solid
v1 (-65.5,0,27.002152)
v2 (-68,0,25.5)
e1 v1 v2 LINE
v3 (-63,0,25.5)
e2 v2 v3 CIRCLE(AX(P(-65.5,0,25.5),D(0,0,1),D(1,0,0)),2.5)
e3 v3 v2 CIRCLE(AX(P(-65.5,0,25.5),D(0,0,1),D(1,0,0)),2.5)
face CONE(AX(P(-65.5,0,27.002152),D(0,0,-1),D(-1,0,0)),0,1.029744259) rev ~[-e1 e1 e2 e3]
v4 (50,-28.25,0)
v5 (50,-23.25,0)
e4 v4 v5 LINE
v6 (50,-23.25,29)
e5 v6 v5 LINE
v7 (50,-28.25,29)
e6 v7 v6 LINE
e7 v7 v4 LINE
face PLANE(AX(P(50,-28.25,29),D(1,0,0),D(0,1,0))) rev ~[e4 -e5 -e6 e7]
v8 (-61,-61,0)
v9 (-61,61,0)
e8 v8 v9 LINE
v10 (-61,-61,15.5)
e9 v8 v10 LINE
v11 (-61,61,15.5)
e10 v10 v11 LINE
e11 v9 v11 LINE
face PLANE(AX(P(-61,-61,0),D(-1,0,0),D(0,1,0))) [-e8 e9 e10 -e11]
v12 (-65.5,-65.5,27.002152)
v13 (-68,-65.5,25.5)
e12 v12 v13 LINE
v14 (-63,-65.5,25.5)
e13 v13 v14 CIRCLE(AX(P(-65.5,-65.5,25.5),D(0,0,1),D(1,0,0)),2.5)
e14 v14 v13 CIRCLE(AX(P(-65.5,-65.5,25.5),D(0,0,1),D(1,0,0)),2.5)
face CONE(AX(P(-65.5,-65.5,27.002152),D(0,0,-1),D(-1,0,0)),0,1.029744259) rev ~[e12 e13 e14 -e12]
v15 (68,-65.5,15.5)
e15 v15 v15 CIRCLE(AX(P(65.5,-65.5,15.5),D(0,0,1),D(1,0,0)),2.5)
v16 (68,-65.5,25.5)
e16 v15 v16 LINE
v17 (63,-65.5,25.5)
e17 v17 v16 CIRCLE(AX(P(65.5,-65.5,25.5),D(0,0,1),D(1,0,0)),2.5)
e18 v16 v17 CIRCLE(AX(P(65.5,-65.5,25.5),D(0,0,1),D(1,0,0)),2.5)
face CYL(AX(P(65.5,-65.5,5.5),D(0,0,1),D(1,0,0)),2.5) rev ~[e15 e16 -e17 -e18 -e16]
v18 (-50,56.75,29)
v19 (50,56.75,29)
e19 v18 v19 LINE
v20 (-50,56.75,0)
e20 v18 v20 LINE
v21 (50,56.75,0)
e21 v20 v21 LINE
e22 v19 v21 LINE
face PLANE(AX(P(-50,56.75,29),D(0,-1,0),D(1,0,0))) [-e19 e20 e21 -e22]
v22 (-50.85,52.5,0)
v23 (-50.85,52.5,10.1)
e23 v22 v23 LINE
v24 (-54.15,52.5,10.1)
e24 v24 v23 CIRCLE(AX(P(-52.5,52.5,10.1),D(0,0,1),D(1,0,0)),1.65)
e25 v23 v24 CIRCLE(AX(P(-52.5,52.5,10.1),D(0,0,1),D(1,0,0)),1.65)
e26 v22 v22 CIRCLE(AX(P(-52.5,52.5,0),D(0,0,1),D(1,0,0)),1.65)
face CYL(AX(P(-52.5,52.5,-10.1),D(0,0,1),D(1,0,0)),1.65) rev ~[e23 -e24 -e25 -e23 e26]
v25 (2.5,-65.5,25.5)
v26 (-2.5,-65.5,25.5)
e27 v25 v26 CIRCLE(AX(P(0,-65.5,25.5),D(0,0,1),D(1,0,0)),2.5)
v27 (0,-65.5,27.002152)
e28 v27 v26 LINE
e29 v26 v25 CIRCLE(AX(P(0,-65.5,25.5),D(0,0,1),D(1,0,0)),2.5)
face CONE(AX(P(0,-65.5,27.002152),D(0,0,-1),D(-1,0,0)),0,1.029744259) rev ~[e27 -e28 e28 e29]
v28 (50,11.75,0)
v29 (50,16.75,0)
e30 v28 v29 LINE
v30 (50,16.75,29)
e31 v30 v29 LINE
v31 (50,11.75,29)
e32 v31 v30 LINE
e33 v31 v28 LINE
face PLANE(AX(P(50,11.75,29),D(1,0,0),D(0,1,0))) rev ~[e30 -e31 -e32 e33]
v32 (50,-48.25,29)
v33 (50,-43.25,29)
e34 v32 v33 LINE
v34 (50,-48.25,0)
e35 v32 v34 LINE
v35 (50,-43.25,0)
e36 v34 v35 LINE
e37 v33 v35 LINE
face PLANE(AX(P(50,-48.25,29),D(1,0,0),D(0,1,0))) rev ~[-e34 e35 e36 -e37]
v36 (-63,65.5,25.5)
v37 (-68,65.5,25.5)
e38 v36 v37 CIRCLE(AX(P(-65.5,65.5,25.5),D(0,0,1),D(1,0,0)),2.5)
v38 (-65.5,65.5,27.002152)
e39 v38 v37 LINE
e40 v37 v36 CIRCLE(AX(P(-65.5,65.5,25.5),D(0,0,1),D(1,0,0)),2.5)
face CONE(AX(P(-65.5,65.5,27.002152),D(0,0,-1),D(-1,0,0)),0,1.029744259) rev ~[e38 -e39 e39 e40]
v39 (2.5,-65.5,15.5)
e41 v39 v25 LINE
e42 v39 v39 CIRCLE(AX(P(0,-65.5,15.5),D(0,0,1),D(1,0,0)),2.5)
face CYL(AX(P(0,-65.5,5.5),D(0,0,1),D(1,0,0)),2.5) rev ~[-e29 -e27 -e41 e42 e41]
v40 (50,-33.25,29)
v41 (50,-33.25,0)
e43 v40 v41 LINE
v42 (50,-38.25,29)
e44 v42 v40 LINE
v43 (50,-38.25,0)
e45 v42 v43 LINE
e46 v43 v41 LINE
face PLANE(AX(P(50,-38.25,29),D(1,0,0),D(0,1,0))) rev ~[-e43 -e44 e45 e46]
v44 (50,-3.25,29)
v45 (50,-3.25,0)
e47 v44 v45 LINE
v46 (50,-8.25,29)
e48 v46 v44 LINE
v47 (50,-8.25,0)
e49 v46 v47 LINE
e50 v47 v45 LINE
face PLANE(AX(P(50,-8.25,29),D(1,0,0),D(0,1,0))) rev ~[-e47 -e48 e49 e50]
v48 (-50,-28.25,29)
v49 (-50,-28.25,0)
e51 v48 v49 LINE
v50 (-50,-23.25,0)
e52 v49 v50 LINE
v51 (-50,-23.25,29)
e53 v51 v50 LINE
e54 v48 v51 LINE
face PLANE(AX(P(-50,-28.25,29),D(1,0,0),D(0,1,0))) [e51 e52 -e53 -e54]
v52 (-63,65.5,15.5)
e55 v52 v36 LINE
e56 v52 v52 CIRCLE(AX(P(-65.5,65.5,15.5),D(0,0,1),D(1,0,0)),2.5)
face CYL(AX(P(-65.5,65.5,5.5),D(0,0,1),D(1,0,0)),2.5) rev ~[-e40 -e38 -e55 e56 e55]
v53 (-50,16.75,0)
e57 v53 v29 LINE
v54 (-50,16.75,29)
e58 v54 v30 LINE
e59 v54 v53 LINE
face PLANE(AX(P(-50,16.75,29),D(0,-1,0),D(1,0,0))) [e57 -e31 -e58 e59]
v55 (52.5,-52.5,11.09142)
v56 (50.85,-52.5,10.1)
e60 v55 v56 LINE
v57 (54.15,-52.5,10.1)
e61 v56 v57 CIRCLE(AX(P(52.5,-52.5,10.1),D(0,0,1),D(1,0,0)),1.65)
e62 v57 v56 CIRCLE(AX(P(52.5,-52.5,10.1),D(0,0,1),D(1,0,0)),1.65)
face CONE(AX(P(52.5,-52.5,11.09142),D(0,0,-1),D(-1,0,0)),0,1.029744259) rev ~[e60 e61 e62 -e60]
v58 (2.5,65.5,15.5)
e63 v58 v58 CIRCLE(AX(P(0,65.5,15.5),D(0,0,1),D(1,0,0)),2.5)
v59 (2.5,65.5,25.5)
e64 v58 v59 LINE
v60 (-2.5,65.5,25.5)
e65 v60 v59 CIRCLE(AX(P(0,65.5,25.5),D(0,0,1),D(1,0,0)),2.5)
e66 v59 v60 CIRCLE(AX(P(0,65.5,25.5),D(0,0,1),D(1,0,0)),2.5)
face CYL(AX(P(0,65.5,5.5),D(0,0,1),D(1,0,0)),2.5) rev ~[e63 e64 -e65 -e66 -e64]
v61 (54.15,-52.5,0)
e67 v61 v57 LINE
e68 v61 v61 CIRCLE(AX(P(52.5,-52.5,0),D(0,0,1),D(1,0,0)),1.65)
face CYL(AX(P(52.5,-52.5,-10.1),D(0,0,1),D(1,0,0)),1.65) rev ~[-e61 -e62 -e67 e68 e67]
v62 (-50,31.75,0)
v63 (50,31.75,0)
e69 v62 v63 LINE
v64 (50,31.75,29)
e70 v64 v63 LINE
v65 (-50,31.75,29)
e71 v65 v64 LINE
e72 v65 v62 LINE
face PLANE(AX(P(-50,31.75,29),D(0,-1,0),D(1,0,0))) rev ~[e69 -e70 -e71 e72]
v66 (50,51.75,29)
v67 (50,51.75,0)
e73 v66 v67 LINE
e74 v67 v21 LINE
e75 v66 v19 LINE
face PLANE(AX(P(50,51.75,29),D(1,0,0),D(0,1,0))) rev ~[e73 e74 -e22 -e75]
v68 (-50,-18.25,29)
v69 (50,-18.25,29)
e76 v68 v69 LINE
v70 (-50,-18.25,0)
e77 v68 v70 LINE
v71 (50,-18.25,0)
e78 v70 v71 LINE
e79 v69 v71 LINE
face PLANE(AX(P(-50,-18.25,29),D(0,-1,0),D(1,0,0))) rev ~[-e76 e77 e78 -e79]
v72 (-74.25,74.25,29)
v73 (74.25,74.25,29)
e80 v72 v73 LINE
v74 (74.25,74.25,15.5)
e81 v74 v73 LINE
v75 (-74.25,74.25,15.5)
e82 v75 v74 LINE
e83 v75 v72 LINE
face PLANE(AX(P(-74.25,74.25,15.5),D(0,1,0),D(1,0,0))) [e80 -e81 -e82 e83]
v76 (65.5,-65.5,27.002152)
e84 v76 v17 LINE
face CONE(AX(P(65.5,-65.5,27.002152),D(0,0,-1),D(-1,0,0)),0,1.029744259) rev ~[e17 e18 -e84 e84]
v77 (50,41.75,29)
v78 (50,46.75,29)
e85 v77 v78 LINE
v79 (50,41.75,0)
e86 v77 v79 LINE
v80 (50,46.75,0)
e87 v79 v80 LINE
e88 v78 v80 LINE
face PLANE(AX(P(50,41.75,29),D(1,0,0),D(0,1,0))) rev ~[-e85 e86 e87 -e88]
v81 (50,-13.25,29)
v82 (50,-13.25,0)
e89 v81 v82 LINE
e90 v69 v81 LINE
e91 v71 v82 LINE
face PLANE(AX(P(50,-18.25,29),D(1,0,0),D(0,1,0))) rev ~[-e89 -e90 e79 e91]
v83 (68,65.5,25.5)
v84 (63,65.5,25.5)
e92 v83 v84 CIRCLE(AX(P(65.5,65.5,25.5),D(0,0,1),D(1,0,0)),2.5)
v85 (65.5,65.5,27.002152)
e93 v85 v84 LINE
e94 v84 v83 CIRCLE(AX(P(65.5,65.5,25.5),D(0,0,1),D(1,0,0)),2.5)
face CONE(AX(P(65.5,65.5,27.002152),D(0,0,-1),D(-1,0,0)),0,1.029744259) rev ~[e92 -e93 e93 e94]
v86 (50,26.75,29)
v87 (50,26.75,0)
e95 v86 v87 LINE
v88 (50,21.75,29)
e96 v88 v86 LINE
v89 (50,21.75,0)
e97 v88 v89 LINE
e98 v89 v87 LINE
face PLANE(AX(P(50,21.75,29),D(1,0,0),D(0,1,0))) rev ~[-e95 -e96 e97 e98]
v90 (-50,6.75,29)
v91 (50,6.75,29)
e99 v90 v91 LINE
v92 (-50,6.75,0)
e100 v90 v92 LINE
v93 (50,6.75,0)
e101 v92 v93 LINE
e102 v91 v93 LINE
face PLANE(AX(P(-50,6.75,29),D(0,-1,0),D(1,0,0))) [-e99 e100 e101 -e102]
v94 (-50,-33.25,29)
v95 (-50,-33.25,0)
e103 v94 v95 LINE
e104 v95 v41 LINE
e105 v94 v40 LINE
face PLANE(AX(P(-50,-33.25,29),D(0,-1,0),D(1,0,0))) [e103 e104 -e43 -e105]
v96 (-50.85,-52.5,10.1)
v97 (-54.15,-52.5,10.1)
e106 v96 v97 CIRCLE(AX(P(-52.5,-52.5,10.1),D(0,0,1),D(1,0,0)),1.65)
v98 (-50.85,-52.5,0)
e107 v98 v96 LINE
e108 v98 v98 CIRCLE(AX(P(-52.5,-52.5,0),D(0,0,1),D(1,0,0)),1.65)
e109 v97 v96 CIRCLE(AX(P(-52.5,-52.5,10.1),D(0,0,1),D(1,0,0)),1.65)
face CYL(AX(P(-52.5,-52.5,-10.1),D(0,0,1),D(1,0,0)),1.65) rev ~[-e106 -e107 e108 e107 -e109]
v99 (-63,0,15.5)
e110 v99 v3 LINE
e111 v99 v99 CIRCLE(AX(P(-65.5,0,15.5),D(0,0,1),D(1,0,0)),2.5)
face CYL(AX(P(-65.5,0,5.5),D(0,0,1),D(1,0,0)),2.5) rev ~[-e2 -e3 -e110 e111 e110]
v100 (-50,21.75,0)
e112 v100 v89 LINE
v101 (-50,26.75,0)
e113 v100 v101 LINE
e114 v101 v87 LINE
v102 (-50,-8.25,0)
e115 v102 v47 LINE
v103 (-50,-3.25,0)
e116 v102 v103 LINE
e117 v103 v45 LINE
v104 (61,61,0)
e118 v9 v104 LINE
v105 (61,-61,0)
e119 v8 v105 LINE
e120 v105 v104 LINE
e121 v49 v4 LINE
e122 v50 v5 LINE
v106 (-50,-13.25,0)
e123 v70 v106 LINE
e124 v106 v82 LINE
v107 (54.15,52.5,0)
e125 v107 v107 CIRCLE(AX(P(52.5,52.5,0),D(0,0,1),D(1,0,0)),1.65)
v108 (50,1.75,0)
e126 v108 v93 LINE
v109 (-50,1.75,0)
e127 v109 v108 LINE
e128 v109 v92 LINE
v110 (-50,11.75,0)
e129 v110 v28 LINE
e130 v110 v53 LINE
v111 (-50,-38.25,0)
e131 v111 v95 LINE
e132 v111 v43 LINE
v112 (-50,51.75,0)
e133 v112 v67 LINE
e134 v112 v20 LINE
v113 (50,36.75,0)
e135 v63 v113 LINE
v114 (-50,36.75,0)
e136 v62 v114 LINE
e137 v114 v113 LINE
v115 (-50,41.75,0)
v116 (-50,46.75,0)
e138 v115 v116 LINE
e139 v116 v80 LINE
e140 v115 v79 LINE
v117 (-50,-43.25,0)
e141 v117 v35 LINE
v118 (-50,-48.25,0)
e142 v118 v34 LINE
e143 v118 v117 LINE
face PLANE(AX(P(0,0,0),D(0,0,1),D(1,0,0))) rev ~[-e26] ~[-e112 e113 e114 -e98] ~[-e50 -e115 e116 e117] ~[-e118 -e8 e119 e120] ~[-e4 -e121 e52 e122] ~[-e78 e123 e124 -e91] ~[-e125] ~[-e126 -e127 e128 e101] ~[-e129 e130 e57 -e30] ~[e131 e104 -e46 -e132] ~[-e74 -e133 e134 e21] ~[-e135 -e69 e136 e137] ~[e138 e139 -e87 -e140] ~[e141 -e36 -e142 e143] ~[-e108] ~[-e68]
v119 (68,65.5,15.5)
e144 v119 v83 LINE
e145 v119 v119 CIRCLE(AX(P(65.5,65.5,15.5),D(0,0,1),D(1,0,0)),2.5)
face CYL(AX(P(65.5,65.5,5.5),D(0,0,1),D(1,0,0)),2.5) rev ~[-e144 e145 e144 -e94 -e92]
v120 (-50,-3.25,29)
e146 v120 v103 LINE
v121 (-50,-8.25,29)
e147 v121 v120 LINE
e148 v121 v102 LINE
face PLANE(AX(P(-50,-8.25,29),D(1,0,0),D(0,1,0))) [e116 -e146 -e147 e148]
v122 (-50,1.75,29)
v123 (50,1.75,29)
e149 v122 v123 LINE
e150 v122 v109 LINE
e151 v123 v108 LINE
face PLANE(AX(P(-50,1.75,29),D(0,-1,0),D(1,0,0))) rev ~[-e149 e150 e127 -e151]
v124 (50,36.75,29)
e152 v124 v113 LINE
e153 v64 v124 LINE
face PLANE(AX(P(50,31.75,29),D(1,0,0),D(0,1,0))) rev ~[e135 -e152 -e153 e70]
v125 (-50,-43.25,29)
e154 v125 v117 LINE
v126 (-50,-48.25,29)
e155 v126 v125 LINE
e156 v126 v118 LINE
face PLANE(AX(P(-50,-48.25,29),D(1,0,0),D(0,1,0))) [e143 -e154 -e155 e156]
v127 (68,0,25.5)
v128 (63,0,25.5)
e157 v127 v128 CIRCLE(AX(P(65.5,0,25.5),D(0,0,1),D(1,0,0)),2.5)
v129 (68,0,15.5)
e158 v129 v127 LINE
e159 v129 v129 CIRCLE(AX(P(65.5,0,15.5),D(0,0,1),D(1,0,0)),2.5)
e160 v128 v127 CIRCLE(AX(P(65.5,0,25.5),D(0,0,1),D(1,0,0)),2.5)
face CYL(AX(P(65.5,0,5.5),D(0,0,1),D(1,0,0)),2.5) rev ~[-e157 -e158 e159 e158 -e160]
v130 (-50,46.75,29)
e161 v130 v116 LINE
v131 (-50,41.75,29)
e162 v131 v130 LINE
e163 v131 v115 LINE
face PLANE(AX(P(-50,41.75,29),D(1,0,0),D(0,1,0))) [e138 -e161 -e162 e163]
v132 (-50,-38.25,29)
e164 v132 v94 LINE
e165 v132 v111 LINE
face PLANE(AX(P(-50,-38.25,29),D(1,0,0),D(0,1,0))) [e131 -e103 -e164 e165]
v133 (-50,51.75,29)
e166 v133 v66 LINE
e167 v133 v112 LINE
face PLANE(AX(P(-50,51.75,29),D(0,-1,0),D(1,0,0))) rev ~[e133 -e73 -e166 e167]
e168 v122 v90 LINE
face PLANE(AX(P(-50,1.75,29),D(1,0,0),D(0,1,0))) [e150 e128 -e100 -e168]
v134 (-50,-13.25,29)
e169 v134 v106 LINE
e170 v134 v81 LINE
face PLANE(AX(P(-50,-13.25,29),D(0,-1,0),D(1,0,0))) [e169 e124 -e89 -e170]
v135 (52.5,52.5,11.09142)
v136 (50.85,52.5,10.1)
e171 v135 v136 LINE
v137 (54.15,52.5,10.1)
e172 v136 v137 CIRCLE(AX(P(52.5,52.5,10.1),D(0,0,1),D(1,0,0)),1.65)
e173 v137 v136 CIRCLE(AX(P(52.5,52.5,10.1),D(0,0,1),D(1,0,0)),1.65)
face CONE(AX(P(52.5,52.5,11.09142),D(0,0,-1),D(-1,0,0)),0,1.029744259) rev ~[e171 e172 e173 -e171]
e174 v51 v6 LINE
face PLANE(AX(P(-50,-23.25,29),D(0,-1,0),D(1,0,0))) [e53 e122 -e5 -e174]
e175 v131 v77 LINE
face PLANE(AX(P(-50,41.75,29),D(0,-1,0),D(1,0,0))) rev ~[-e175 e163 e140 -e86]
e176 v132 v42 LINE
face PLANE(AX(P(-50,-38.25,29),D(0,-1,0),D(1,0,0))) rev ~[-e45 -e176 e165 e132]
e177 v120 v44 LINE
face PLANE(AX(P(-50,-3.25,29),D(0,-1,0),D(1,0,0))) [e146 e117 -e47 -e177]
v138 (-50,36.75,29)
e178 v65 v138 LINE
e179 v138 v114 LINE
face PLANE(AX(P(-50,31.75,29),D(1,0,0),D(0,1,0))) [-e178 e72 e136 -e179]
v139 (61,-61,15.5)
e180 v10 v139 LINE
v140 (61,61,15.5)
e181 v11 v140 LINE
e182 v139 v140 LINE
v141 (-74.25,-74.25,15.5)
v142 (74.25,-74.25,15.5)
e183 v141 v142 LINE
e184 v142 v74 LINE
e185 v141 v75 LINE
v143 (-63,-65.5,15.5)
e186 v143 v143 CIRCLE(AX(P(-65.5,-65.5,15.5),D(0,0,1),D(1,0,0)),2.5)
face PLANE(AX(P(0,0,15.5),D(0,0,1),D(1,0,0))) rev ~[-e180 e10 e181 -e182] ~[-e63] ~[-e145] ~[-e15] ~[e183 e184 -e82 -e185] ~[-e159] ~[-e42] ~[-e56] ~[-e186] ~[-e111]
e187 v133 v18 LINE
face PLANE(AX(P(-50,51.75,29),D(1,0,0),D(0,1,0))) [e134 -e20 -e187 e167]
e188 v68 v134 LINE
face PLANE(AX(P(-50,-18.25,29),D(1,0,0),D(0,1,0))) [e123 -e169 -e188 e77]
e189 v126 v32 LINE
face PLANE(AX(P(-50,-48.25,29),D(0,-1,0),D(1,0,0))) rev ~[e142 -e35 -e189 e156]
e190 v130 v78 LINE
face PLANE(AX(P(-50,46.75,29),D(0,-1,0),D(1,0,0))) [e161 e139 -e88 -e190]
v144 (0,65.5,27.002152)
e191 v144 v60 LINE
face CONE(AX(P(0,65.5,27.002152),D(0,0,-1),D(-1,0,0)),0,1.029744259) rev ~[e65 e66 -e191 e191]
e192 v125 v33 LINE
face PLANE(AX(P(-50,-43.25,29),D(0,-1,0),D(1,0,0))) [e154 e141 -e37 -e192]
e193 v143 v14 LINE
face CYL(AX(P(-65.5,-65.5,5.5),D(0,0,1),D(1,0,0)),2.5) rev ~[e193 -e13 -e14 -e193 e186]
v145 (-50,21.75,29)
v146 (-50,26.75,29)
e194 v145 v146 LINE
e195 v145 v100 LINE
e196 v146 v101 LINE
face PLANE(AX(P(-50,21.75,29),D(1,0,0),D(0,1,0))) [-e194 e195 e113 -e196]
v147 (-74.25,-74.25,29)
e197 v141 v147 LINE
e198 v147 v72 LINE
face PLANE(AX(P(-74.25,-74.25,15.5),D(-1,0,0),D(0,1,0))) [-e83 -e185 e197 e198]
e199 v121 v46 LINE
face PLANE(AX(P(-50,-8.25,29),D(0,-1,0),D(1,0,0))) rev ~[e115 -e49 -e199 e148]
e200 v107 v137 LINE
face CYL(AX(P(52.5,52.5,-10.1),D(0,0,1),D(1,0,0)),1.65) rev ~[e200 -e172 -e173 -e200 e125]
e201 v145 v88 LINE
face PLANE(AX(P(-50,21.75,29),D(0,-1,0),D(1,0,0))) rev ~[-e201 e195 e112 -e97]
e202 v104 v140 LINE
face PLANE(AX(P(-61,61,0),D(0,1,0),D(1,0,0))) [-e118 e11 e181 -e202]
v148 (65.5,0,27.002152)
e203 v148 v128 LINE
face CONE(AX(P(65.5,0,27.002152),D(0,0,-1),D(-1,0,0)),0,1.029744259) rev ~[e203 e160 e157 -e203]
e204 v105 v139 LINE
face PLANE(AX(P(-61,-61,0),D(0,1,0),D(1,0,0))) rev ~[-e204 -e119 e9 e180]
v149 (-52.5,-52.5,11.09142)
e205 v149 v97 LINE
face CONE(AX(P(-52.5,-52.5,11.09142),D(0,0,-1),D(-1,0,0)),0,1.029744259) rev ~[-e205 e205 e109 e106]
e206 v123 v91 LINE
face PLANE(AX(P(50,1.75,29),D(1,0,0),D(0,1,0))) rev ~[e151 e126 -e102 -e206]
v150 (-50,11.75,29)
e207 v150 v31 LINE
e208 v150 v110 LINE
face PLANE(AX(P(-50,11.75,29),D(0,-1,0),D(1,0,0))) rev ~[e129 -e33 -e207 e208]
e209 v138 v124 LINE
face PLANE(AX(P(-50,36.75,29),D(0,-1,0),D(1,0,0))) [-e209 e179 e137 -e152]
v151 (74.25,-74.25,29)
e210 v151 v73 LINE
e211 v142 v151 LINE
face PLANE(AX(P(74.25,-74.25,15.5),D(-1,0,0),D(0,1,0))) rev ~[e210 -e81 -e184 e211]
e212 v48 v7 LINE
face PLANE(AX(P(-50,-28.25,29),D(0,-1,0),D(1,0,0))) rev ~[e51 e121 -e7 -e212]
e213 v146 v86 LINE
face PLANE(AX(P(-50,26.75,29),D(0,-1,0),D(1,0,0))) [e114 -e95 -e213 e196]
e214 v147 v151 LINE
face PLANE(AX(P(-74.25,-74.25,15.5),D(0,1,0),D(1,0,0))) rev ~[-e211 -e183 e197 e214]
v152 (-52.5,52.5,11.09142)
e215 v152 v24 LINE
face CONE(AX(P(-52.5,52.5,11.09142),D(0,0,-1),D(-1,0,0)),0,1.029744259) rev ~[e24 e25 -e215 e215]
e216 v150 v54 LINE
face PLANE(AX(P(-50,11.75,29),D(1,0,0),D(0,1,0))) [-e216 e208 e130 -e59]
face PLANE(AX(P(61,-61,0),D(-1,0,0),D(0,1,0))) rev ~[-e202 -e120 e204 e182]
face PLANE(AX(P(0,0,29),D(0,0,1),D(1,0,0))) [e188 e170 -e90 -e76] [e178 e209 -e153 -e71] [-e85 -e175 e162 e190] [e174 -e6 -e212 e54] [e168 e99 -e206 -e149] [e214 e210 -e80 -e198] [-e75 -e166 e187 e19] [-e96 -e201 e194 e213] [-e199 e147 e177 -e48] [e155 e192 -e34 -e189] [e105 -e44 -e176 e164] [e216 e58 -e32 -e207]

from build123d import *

# Parameters (mm, degrees)
SKETCH_1_W             = 122
SKETCH_1_H             = 122
EXTRUDE_1_DEPTH        = 15.5
SKETCH_2_W             = 148.5
SKETCH_2_H             = 148.5
EXTRUDE_2_DEPTH        = 13.5
SKETCH_3_W             = 100
SKETCH_3_H             = 5
CUT_EXTRUDE_1_DEPTH    = 109.936334618
PATTERN_LINEAR_1_COUNT = 11
PATTERN_LINEAR_1_PITCH = 10
MM_1_D                 = 5
MM_1_DEPTH             = 10
MM_1_TIP               = 1.502151548
HOLE_WIZARD_M4_1_D     = 3.3
HOLE_WIZARD_M4_1_DEPTH = 10.1
HOLE_WIZARD_M4_1_TIP   = 0.991420021


with BuildPart() as part:
    # 草图1 → 凸台-拉伸1 (new body)
    with BuildSketch(Plane.XY):
        Rectangle(SKETCH_1_W, SKETCH_1_H)
    extrude(amount=EXTRUDE_1_DEPTH)

    # 草图2 → 凸台-拉伸2 (add)
    with BuildSketch(Plane.XY.offset(15.5)):
        Rectangle(SKETCH_2_W, SKETCH_2_H)
    extrude(amount=EXTRUDE_2_DEPTH)

    # 草图3 → 切除-拉伸1 (cut, through all)
    with BuildSketch(Plane.XY.offset(29)):
        with Locations((0, 54.25)):
            Rectangle(SKETCH_3_W, SKETCH_3_H)
    cut_extrude_1 = extrude(amount=-CUT_EXTRUDE_1_DEPTH, mode=Mode.SUBTRACT)

    # 阵列(线性)1: 切除-拉伸1 ×11
    with Locations(*[(0, -i * PATTERN_LINEAR_1_PITCH, 0) for i in range(1, PATTERN_LINEAR_1_COUNT)]):
        add(cut_extrude_1, mode=Mode.SUBTRACT)

    # 大小mm 暗销孔1
    with Locations(Plane(origin=(0, 0, 15.5), x_dir=(-1, 0, 0), z_dir=(0, 0, -1))):
        with Locations((-65.5, 65.5), (0, 65.5), (65.5, 65.5), (65.5, 0), (-65.5, 0), (-65.5, -65.5), (0, -65.5), (65.5, -65.5)):
            Hole(MM_1_D / 2, depth=MM_1_DEPTH)
            with Locations((0, 0, -(MM_1_DEPTH + MM_1_TIP / 2))):  # 118° drill point
                Cone(0, MM_1_D / 2, MM_1_TIP, mode=Mode.SUBTRACT)

    # M4 螺纹孔1
    with Locations(Plane(origin=(0, 0, 0), x_dir=(-1, 0, 0), z_dir=(0, 0, -1))):
        with Locations((-52.5, 52.5), (52.5, 52.5), (52.5, -52.5), (-52.5, -52.5)):
            Hole(HOLE_WIZARD_M4_1_D / 2, depth=HOLE_WIZARD_M4_1_DEPTH)
            with Locations((0, 0, -(HOLE_WIZARD_M4_1_DEPTH + HOLE_WIZARD_M4_1_TIP / 2))):  # 118° drill point
                Cone(0, HOLE_WIZARD_M4_1_D / 2, HOLE_WIZARD_M4_1_TIP, mode=Mode.SUBTRACT)


solid = part.part
